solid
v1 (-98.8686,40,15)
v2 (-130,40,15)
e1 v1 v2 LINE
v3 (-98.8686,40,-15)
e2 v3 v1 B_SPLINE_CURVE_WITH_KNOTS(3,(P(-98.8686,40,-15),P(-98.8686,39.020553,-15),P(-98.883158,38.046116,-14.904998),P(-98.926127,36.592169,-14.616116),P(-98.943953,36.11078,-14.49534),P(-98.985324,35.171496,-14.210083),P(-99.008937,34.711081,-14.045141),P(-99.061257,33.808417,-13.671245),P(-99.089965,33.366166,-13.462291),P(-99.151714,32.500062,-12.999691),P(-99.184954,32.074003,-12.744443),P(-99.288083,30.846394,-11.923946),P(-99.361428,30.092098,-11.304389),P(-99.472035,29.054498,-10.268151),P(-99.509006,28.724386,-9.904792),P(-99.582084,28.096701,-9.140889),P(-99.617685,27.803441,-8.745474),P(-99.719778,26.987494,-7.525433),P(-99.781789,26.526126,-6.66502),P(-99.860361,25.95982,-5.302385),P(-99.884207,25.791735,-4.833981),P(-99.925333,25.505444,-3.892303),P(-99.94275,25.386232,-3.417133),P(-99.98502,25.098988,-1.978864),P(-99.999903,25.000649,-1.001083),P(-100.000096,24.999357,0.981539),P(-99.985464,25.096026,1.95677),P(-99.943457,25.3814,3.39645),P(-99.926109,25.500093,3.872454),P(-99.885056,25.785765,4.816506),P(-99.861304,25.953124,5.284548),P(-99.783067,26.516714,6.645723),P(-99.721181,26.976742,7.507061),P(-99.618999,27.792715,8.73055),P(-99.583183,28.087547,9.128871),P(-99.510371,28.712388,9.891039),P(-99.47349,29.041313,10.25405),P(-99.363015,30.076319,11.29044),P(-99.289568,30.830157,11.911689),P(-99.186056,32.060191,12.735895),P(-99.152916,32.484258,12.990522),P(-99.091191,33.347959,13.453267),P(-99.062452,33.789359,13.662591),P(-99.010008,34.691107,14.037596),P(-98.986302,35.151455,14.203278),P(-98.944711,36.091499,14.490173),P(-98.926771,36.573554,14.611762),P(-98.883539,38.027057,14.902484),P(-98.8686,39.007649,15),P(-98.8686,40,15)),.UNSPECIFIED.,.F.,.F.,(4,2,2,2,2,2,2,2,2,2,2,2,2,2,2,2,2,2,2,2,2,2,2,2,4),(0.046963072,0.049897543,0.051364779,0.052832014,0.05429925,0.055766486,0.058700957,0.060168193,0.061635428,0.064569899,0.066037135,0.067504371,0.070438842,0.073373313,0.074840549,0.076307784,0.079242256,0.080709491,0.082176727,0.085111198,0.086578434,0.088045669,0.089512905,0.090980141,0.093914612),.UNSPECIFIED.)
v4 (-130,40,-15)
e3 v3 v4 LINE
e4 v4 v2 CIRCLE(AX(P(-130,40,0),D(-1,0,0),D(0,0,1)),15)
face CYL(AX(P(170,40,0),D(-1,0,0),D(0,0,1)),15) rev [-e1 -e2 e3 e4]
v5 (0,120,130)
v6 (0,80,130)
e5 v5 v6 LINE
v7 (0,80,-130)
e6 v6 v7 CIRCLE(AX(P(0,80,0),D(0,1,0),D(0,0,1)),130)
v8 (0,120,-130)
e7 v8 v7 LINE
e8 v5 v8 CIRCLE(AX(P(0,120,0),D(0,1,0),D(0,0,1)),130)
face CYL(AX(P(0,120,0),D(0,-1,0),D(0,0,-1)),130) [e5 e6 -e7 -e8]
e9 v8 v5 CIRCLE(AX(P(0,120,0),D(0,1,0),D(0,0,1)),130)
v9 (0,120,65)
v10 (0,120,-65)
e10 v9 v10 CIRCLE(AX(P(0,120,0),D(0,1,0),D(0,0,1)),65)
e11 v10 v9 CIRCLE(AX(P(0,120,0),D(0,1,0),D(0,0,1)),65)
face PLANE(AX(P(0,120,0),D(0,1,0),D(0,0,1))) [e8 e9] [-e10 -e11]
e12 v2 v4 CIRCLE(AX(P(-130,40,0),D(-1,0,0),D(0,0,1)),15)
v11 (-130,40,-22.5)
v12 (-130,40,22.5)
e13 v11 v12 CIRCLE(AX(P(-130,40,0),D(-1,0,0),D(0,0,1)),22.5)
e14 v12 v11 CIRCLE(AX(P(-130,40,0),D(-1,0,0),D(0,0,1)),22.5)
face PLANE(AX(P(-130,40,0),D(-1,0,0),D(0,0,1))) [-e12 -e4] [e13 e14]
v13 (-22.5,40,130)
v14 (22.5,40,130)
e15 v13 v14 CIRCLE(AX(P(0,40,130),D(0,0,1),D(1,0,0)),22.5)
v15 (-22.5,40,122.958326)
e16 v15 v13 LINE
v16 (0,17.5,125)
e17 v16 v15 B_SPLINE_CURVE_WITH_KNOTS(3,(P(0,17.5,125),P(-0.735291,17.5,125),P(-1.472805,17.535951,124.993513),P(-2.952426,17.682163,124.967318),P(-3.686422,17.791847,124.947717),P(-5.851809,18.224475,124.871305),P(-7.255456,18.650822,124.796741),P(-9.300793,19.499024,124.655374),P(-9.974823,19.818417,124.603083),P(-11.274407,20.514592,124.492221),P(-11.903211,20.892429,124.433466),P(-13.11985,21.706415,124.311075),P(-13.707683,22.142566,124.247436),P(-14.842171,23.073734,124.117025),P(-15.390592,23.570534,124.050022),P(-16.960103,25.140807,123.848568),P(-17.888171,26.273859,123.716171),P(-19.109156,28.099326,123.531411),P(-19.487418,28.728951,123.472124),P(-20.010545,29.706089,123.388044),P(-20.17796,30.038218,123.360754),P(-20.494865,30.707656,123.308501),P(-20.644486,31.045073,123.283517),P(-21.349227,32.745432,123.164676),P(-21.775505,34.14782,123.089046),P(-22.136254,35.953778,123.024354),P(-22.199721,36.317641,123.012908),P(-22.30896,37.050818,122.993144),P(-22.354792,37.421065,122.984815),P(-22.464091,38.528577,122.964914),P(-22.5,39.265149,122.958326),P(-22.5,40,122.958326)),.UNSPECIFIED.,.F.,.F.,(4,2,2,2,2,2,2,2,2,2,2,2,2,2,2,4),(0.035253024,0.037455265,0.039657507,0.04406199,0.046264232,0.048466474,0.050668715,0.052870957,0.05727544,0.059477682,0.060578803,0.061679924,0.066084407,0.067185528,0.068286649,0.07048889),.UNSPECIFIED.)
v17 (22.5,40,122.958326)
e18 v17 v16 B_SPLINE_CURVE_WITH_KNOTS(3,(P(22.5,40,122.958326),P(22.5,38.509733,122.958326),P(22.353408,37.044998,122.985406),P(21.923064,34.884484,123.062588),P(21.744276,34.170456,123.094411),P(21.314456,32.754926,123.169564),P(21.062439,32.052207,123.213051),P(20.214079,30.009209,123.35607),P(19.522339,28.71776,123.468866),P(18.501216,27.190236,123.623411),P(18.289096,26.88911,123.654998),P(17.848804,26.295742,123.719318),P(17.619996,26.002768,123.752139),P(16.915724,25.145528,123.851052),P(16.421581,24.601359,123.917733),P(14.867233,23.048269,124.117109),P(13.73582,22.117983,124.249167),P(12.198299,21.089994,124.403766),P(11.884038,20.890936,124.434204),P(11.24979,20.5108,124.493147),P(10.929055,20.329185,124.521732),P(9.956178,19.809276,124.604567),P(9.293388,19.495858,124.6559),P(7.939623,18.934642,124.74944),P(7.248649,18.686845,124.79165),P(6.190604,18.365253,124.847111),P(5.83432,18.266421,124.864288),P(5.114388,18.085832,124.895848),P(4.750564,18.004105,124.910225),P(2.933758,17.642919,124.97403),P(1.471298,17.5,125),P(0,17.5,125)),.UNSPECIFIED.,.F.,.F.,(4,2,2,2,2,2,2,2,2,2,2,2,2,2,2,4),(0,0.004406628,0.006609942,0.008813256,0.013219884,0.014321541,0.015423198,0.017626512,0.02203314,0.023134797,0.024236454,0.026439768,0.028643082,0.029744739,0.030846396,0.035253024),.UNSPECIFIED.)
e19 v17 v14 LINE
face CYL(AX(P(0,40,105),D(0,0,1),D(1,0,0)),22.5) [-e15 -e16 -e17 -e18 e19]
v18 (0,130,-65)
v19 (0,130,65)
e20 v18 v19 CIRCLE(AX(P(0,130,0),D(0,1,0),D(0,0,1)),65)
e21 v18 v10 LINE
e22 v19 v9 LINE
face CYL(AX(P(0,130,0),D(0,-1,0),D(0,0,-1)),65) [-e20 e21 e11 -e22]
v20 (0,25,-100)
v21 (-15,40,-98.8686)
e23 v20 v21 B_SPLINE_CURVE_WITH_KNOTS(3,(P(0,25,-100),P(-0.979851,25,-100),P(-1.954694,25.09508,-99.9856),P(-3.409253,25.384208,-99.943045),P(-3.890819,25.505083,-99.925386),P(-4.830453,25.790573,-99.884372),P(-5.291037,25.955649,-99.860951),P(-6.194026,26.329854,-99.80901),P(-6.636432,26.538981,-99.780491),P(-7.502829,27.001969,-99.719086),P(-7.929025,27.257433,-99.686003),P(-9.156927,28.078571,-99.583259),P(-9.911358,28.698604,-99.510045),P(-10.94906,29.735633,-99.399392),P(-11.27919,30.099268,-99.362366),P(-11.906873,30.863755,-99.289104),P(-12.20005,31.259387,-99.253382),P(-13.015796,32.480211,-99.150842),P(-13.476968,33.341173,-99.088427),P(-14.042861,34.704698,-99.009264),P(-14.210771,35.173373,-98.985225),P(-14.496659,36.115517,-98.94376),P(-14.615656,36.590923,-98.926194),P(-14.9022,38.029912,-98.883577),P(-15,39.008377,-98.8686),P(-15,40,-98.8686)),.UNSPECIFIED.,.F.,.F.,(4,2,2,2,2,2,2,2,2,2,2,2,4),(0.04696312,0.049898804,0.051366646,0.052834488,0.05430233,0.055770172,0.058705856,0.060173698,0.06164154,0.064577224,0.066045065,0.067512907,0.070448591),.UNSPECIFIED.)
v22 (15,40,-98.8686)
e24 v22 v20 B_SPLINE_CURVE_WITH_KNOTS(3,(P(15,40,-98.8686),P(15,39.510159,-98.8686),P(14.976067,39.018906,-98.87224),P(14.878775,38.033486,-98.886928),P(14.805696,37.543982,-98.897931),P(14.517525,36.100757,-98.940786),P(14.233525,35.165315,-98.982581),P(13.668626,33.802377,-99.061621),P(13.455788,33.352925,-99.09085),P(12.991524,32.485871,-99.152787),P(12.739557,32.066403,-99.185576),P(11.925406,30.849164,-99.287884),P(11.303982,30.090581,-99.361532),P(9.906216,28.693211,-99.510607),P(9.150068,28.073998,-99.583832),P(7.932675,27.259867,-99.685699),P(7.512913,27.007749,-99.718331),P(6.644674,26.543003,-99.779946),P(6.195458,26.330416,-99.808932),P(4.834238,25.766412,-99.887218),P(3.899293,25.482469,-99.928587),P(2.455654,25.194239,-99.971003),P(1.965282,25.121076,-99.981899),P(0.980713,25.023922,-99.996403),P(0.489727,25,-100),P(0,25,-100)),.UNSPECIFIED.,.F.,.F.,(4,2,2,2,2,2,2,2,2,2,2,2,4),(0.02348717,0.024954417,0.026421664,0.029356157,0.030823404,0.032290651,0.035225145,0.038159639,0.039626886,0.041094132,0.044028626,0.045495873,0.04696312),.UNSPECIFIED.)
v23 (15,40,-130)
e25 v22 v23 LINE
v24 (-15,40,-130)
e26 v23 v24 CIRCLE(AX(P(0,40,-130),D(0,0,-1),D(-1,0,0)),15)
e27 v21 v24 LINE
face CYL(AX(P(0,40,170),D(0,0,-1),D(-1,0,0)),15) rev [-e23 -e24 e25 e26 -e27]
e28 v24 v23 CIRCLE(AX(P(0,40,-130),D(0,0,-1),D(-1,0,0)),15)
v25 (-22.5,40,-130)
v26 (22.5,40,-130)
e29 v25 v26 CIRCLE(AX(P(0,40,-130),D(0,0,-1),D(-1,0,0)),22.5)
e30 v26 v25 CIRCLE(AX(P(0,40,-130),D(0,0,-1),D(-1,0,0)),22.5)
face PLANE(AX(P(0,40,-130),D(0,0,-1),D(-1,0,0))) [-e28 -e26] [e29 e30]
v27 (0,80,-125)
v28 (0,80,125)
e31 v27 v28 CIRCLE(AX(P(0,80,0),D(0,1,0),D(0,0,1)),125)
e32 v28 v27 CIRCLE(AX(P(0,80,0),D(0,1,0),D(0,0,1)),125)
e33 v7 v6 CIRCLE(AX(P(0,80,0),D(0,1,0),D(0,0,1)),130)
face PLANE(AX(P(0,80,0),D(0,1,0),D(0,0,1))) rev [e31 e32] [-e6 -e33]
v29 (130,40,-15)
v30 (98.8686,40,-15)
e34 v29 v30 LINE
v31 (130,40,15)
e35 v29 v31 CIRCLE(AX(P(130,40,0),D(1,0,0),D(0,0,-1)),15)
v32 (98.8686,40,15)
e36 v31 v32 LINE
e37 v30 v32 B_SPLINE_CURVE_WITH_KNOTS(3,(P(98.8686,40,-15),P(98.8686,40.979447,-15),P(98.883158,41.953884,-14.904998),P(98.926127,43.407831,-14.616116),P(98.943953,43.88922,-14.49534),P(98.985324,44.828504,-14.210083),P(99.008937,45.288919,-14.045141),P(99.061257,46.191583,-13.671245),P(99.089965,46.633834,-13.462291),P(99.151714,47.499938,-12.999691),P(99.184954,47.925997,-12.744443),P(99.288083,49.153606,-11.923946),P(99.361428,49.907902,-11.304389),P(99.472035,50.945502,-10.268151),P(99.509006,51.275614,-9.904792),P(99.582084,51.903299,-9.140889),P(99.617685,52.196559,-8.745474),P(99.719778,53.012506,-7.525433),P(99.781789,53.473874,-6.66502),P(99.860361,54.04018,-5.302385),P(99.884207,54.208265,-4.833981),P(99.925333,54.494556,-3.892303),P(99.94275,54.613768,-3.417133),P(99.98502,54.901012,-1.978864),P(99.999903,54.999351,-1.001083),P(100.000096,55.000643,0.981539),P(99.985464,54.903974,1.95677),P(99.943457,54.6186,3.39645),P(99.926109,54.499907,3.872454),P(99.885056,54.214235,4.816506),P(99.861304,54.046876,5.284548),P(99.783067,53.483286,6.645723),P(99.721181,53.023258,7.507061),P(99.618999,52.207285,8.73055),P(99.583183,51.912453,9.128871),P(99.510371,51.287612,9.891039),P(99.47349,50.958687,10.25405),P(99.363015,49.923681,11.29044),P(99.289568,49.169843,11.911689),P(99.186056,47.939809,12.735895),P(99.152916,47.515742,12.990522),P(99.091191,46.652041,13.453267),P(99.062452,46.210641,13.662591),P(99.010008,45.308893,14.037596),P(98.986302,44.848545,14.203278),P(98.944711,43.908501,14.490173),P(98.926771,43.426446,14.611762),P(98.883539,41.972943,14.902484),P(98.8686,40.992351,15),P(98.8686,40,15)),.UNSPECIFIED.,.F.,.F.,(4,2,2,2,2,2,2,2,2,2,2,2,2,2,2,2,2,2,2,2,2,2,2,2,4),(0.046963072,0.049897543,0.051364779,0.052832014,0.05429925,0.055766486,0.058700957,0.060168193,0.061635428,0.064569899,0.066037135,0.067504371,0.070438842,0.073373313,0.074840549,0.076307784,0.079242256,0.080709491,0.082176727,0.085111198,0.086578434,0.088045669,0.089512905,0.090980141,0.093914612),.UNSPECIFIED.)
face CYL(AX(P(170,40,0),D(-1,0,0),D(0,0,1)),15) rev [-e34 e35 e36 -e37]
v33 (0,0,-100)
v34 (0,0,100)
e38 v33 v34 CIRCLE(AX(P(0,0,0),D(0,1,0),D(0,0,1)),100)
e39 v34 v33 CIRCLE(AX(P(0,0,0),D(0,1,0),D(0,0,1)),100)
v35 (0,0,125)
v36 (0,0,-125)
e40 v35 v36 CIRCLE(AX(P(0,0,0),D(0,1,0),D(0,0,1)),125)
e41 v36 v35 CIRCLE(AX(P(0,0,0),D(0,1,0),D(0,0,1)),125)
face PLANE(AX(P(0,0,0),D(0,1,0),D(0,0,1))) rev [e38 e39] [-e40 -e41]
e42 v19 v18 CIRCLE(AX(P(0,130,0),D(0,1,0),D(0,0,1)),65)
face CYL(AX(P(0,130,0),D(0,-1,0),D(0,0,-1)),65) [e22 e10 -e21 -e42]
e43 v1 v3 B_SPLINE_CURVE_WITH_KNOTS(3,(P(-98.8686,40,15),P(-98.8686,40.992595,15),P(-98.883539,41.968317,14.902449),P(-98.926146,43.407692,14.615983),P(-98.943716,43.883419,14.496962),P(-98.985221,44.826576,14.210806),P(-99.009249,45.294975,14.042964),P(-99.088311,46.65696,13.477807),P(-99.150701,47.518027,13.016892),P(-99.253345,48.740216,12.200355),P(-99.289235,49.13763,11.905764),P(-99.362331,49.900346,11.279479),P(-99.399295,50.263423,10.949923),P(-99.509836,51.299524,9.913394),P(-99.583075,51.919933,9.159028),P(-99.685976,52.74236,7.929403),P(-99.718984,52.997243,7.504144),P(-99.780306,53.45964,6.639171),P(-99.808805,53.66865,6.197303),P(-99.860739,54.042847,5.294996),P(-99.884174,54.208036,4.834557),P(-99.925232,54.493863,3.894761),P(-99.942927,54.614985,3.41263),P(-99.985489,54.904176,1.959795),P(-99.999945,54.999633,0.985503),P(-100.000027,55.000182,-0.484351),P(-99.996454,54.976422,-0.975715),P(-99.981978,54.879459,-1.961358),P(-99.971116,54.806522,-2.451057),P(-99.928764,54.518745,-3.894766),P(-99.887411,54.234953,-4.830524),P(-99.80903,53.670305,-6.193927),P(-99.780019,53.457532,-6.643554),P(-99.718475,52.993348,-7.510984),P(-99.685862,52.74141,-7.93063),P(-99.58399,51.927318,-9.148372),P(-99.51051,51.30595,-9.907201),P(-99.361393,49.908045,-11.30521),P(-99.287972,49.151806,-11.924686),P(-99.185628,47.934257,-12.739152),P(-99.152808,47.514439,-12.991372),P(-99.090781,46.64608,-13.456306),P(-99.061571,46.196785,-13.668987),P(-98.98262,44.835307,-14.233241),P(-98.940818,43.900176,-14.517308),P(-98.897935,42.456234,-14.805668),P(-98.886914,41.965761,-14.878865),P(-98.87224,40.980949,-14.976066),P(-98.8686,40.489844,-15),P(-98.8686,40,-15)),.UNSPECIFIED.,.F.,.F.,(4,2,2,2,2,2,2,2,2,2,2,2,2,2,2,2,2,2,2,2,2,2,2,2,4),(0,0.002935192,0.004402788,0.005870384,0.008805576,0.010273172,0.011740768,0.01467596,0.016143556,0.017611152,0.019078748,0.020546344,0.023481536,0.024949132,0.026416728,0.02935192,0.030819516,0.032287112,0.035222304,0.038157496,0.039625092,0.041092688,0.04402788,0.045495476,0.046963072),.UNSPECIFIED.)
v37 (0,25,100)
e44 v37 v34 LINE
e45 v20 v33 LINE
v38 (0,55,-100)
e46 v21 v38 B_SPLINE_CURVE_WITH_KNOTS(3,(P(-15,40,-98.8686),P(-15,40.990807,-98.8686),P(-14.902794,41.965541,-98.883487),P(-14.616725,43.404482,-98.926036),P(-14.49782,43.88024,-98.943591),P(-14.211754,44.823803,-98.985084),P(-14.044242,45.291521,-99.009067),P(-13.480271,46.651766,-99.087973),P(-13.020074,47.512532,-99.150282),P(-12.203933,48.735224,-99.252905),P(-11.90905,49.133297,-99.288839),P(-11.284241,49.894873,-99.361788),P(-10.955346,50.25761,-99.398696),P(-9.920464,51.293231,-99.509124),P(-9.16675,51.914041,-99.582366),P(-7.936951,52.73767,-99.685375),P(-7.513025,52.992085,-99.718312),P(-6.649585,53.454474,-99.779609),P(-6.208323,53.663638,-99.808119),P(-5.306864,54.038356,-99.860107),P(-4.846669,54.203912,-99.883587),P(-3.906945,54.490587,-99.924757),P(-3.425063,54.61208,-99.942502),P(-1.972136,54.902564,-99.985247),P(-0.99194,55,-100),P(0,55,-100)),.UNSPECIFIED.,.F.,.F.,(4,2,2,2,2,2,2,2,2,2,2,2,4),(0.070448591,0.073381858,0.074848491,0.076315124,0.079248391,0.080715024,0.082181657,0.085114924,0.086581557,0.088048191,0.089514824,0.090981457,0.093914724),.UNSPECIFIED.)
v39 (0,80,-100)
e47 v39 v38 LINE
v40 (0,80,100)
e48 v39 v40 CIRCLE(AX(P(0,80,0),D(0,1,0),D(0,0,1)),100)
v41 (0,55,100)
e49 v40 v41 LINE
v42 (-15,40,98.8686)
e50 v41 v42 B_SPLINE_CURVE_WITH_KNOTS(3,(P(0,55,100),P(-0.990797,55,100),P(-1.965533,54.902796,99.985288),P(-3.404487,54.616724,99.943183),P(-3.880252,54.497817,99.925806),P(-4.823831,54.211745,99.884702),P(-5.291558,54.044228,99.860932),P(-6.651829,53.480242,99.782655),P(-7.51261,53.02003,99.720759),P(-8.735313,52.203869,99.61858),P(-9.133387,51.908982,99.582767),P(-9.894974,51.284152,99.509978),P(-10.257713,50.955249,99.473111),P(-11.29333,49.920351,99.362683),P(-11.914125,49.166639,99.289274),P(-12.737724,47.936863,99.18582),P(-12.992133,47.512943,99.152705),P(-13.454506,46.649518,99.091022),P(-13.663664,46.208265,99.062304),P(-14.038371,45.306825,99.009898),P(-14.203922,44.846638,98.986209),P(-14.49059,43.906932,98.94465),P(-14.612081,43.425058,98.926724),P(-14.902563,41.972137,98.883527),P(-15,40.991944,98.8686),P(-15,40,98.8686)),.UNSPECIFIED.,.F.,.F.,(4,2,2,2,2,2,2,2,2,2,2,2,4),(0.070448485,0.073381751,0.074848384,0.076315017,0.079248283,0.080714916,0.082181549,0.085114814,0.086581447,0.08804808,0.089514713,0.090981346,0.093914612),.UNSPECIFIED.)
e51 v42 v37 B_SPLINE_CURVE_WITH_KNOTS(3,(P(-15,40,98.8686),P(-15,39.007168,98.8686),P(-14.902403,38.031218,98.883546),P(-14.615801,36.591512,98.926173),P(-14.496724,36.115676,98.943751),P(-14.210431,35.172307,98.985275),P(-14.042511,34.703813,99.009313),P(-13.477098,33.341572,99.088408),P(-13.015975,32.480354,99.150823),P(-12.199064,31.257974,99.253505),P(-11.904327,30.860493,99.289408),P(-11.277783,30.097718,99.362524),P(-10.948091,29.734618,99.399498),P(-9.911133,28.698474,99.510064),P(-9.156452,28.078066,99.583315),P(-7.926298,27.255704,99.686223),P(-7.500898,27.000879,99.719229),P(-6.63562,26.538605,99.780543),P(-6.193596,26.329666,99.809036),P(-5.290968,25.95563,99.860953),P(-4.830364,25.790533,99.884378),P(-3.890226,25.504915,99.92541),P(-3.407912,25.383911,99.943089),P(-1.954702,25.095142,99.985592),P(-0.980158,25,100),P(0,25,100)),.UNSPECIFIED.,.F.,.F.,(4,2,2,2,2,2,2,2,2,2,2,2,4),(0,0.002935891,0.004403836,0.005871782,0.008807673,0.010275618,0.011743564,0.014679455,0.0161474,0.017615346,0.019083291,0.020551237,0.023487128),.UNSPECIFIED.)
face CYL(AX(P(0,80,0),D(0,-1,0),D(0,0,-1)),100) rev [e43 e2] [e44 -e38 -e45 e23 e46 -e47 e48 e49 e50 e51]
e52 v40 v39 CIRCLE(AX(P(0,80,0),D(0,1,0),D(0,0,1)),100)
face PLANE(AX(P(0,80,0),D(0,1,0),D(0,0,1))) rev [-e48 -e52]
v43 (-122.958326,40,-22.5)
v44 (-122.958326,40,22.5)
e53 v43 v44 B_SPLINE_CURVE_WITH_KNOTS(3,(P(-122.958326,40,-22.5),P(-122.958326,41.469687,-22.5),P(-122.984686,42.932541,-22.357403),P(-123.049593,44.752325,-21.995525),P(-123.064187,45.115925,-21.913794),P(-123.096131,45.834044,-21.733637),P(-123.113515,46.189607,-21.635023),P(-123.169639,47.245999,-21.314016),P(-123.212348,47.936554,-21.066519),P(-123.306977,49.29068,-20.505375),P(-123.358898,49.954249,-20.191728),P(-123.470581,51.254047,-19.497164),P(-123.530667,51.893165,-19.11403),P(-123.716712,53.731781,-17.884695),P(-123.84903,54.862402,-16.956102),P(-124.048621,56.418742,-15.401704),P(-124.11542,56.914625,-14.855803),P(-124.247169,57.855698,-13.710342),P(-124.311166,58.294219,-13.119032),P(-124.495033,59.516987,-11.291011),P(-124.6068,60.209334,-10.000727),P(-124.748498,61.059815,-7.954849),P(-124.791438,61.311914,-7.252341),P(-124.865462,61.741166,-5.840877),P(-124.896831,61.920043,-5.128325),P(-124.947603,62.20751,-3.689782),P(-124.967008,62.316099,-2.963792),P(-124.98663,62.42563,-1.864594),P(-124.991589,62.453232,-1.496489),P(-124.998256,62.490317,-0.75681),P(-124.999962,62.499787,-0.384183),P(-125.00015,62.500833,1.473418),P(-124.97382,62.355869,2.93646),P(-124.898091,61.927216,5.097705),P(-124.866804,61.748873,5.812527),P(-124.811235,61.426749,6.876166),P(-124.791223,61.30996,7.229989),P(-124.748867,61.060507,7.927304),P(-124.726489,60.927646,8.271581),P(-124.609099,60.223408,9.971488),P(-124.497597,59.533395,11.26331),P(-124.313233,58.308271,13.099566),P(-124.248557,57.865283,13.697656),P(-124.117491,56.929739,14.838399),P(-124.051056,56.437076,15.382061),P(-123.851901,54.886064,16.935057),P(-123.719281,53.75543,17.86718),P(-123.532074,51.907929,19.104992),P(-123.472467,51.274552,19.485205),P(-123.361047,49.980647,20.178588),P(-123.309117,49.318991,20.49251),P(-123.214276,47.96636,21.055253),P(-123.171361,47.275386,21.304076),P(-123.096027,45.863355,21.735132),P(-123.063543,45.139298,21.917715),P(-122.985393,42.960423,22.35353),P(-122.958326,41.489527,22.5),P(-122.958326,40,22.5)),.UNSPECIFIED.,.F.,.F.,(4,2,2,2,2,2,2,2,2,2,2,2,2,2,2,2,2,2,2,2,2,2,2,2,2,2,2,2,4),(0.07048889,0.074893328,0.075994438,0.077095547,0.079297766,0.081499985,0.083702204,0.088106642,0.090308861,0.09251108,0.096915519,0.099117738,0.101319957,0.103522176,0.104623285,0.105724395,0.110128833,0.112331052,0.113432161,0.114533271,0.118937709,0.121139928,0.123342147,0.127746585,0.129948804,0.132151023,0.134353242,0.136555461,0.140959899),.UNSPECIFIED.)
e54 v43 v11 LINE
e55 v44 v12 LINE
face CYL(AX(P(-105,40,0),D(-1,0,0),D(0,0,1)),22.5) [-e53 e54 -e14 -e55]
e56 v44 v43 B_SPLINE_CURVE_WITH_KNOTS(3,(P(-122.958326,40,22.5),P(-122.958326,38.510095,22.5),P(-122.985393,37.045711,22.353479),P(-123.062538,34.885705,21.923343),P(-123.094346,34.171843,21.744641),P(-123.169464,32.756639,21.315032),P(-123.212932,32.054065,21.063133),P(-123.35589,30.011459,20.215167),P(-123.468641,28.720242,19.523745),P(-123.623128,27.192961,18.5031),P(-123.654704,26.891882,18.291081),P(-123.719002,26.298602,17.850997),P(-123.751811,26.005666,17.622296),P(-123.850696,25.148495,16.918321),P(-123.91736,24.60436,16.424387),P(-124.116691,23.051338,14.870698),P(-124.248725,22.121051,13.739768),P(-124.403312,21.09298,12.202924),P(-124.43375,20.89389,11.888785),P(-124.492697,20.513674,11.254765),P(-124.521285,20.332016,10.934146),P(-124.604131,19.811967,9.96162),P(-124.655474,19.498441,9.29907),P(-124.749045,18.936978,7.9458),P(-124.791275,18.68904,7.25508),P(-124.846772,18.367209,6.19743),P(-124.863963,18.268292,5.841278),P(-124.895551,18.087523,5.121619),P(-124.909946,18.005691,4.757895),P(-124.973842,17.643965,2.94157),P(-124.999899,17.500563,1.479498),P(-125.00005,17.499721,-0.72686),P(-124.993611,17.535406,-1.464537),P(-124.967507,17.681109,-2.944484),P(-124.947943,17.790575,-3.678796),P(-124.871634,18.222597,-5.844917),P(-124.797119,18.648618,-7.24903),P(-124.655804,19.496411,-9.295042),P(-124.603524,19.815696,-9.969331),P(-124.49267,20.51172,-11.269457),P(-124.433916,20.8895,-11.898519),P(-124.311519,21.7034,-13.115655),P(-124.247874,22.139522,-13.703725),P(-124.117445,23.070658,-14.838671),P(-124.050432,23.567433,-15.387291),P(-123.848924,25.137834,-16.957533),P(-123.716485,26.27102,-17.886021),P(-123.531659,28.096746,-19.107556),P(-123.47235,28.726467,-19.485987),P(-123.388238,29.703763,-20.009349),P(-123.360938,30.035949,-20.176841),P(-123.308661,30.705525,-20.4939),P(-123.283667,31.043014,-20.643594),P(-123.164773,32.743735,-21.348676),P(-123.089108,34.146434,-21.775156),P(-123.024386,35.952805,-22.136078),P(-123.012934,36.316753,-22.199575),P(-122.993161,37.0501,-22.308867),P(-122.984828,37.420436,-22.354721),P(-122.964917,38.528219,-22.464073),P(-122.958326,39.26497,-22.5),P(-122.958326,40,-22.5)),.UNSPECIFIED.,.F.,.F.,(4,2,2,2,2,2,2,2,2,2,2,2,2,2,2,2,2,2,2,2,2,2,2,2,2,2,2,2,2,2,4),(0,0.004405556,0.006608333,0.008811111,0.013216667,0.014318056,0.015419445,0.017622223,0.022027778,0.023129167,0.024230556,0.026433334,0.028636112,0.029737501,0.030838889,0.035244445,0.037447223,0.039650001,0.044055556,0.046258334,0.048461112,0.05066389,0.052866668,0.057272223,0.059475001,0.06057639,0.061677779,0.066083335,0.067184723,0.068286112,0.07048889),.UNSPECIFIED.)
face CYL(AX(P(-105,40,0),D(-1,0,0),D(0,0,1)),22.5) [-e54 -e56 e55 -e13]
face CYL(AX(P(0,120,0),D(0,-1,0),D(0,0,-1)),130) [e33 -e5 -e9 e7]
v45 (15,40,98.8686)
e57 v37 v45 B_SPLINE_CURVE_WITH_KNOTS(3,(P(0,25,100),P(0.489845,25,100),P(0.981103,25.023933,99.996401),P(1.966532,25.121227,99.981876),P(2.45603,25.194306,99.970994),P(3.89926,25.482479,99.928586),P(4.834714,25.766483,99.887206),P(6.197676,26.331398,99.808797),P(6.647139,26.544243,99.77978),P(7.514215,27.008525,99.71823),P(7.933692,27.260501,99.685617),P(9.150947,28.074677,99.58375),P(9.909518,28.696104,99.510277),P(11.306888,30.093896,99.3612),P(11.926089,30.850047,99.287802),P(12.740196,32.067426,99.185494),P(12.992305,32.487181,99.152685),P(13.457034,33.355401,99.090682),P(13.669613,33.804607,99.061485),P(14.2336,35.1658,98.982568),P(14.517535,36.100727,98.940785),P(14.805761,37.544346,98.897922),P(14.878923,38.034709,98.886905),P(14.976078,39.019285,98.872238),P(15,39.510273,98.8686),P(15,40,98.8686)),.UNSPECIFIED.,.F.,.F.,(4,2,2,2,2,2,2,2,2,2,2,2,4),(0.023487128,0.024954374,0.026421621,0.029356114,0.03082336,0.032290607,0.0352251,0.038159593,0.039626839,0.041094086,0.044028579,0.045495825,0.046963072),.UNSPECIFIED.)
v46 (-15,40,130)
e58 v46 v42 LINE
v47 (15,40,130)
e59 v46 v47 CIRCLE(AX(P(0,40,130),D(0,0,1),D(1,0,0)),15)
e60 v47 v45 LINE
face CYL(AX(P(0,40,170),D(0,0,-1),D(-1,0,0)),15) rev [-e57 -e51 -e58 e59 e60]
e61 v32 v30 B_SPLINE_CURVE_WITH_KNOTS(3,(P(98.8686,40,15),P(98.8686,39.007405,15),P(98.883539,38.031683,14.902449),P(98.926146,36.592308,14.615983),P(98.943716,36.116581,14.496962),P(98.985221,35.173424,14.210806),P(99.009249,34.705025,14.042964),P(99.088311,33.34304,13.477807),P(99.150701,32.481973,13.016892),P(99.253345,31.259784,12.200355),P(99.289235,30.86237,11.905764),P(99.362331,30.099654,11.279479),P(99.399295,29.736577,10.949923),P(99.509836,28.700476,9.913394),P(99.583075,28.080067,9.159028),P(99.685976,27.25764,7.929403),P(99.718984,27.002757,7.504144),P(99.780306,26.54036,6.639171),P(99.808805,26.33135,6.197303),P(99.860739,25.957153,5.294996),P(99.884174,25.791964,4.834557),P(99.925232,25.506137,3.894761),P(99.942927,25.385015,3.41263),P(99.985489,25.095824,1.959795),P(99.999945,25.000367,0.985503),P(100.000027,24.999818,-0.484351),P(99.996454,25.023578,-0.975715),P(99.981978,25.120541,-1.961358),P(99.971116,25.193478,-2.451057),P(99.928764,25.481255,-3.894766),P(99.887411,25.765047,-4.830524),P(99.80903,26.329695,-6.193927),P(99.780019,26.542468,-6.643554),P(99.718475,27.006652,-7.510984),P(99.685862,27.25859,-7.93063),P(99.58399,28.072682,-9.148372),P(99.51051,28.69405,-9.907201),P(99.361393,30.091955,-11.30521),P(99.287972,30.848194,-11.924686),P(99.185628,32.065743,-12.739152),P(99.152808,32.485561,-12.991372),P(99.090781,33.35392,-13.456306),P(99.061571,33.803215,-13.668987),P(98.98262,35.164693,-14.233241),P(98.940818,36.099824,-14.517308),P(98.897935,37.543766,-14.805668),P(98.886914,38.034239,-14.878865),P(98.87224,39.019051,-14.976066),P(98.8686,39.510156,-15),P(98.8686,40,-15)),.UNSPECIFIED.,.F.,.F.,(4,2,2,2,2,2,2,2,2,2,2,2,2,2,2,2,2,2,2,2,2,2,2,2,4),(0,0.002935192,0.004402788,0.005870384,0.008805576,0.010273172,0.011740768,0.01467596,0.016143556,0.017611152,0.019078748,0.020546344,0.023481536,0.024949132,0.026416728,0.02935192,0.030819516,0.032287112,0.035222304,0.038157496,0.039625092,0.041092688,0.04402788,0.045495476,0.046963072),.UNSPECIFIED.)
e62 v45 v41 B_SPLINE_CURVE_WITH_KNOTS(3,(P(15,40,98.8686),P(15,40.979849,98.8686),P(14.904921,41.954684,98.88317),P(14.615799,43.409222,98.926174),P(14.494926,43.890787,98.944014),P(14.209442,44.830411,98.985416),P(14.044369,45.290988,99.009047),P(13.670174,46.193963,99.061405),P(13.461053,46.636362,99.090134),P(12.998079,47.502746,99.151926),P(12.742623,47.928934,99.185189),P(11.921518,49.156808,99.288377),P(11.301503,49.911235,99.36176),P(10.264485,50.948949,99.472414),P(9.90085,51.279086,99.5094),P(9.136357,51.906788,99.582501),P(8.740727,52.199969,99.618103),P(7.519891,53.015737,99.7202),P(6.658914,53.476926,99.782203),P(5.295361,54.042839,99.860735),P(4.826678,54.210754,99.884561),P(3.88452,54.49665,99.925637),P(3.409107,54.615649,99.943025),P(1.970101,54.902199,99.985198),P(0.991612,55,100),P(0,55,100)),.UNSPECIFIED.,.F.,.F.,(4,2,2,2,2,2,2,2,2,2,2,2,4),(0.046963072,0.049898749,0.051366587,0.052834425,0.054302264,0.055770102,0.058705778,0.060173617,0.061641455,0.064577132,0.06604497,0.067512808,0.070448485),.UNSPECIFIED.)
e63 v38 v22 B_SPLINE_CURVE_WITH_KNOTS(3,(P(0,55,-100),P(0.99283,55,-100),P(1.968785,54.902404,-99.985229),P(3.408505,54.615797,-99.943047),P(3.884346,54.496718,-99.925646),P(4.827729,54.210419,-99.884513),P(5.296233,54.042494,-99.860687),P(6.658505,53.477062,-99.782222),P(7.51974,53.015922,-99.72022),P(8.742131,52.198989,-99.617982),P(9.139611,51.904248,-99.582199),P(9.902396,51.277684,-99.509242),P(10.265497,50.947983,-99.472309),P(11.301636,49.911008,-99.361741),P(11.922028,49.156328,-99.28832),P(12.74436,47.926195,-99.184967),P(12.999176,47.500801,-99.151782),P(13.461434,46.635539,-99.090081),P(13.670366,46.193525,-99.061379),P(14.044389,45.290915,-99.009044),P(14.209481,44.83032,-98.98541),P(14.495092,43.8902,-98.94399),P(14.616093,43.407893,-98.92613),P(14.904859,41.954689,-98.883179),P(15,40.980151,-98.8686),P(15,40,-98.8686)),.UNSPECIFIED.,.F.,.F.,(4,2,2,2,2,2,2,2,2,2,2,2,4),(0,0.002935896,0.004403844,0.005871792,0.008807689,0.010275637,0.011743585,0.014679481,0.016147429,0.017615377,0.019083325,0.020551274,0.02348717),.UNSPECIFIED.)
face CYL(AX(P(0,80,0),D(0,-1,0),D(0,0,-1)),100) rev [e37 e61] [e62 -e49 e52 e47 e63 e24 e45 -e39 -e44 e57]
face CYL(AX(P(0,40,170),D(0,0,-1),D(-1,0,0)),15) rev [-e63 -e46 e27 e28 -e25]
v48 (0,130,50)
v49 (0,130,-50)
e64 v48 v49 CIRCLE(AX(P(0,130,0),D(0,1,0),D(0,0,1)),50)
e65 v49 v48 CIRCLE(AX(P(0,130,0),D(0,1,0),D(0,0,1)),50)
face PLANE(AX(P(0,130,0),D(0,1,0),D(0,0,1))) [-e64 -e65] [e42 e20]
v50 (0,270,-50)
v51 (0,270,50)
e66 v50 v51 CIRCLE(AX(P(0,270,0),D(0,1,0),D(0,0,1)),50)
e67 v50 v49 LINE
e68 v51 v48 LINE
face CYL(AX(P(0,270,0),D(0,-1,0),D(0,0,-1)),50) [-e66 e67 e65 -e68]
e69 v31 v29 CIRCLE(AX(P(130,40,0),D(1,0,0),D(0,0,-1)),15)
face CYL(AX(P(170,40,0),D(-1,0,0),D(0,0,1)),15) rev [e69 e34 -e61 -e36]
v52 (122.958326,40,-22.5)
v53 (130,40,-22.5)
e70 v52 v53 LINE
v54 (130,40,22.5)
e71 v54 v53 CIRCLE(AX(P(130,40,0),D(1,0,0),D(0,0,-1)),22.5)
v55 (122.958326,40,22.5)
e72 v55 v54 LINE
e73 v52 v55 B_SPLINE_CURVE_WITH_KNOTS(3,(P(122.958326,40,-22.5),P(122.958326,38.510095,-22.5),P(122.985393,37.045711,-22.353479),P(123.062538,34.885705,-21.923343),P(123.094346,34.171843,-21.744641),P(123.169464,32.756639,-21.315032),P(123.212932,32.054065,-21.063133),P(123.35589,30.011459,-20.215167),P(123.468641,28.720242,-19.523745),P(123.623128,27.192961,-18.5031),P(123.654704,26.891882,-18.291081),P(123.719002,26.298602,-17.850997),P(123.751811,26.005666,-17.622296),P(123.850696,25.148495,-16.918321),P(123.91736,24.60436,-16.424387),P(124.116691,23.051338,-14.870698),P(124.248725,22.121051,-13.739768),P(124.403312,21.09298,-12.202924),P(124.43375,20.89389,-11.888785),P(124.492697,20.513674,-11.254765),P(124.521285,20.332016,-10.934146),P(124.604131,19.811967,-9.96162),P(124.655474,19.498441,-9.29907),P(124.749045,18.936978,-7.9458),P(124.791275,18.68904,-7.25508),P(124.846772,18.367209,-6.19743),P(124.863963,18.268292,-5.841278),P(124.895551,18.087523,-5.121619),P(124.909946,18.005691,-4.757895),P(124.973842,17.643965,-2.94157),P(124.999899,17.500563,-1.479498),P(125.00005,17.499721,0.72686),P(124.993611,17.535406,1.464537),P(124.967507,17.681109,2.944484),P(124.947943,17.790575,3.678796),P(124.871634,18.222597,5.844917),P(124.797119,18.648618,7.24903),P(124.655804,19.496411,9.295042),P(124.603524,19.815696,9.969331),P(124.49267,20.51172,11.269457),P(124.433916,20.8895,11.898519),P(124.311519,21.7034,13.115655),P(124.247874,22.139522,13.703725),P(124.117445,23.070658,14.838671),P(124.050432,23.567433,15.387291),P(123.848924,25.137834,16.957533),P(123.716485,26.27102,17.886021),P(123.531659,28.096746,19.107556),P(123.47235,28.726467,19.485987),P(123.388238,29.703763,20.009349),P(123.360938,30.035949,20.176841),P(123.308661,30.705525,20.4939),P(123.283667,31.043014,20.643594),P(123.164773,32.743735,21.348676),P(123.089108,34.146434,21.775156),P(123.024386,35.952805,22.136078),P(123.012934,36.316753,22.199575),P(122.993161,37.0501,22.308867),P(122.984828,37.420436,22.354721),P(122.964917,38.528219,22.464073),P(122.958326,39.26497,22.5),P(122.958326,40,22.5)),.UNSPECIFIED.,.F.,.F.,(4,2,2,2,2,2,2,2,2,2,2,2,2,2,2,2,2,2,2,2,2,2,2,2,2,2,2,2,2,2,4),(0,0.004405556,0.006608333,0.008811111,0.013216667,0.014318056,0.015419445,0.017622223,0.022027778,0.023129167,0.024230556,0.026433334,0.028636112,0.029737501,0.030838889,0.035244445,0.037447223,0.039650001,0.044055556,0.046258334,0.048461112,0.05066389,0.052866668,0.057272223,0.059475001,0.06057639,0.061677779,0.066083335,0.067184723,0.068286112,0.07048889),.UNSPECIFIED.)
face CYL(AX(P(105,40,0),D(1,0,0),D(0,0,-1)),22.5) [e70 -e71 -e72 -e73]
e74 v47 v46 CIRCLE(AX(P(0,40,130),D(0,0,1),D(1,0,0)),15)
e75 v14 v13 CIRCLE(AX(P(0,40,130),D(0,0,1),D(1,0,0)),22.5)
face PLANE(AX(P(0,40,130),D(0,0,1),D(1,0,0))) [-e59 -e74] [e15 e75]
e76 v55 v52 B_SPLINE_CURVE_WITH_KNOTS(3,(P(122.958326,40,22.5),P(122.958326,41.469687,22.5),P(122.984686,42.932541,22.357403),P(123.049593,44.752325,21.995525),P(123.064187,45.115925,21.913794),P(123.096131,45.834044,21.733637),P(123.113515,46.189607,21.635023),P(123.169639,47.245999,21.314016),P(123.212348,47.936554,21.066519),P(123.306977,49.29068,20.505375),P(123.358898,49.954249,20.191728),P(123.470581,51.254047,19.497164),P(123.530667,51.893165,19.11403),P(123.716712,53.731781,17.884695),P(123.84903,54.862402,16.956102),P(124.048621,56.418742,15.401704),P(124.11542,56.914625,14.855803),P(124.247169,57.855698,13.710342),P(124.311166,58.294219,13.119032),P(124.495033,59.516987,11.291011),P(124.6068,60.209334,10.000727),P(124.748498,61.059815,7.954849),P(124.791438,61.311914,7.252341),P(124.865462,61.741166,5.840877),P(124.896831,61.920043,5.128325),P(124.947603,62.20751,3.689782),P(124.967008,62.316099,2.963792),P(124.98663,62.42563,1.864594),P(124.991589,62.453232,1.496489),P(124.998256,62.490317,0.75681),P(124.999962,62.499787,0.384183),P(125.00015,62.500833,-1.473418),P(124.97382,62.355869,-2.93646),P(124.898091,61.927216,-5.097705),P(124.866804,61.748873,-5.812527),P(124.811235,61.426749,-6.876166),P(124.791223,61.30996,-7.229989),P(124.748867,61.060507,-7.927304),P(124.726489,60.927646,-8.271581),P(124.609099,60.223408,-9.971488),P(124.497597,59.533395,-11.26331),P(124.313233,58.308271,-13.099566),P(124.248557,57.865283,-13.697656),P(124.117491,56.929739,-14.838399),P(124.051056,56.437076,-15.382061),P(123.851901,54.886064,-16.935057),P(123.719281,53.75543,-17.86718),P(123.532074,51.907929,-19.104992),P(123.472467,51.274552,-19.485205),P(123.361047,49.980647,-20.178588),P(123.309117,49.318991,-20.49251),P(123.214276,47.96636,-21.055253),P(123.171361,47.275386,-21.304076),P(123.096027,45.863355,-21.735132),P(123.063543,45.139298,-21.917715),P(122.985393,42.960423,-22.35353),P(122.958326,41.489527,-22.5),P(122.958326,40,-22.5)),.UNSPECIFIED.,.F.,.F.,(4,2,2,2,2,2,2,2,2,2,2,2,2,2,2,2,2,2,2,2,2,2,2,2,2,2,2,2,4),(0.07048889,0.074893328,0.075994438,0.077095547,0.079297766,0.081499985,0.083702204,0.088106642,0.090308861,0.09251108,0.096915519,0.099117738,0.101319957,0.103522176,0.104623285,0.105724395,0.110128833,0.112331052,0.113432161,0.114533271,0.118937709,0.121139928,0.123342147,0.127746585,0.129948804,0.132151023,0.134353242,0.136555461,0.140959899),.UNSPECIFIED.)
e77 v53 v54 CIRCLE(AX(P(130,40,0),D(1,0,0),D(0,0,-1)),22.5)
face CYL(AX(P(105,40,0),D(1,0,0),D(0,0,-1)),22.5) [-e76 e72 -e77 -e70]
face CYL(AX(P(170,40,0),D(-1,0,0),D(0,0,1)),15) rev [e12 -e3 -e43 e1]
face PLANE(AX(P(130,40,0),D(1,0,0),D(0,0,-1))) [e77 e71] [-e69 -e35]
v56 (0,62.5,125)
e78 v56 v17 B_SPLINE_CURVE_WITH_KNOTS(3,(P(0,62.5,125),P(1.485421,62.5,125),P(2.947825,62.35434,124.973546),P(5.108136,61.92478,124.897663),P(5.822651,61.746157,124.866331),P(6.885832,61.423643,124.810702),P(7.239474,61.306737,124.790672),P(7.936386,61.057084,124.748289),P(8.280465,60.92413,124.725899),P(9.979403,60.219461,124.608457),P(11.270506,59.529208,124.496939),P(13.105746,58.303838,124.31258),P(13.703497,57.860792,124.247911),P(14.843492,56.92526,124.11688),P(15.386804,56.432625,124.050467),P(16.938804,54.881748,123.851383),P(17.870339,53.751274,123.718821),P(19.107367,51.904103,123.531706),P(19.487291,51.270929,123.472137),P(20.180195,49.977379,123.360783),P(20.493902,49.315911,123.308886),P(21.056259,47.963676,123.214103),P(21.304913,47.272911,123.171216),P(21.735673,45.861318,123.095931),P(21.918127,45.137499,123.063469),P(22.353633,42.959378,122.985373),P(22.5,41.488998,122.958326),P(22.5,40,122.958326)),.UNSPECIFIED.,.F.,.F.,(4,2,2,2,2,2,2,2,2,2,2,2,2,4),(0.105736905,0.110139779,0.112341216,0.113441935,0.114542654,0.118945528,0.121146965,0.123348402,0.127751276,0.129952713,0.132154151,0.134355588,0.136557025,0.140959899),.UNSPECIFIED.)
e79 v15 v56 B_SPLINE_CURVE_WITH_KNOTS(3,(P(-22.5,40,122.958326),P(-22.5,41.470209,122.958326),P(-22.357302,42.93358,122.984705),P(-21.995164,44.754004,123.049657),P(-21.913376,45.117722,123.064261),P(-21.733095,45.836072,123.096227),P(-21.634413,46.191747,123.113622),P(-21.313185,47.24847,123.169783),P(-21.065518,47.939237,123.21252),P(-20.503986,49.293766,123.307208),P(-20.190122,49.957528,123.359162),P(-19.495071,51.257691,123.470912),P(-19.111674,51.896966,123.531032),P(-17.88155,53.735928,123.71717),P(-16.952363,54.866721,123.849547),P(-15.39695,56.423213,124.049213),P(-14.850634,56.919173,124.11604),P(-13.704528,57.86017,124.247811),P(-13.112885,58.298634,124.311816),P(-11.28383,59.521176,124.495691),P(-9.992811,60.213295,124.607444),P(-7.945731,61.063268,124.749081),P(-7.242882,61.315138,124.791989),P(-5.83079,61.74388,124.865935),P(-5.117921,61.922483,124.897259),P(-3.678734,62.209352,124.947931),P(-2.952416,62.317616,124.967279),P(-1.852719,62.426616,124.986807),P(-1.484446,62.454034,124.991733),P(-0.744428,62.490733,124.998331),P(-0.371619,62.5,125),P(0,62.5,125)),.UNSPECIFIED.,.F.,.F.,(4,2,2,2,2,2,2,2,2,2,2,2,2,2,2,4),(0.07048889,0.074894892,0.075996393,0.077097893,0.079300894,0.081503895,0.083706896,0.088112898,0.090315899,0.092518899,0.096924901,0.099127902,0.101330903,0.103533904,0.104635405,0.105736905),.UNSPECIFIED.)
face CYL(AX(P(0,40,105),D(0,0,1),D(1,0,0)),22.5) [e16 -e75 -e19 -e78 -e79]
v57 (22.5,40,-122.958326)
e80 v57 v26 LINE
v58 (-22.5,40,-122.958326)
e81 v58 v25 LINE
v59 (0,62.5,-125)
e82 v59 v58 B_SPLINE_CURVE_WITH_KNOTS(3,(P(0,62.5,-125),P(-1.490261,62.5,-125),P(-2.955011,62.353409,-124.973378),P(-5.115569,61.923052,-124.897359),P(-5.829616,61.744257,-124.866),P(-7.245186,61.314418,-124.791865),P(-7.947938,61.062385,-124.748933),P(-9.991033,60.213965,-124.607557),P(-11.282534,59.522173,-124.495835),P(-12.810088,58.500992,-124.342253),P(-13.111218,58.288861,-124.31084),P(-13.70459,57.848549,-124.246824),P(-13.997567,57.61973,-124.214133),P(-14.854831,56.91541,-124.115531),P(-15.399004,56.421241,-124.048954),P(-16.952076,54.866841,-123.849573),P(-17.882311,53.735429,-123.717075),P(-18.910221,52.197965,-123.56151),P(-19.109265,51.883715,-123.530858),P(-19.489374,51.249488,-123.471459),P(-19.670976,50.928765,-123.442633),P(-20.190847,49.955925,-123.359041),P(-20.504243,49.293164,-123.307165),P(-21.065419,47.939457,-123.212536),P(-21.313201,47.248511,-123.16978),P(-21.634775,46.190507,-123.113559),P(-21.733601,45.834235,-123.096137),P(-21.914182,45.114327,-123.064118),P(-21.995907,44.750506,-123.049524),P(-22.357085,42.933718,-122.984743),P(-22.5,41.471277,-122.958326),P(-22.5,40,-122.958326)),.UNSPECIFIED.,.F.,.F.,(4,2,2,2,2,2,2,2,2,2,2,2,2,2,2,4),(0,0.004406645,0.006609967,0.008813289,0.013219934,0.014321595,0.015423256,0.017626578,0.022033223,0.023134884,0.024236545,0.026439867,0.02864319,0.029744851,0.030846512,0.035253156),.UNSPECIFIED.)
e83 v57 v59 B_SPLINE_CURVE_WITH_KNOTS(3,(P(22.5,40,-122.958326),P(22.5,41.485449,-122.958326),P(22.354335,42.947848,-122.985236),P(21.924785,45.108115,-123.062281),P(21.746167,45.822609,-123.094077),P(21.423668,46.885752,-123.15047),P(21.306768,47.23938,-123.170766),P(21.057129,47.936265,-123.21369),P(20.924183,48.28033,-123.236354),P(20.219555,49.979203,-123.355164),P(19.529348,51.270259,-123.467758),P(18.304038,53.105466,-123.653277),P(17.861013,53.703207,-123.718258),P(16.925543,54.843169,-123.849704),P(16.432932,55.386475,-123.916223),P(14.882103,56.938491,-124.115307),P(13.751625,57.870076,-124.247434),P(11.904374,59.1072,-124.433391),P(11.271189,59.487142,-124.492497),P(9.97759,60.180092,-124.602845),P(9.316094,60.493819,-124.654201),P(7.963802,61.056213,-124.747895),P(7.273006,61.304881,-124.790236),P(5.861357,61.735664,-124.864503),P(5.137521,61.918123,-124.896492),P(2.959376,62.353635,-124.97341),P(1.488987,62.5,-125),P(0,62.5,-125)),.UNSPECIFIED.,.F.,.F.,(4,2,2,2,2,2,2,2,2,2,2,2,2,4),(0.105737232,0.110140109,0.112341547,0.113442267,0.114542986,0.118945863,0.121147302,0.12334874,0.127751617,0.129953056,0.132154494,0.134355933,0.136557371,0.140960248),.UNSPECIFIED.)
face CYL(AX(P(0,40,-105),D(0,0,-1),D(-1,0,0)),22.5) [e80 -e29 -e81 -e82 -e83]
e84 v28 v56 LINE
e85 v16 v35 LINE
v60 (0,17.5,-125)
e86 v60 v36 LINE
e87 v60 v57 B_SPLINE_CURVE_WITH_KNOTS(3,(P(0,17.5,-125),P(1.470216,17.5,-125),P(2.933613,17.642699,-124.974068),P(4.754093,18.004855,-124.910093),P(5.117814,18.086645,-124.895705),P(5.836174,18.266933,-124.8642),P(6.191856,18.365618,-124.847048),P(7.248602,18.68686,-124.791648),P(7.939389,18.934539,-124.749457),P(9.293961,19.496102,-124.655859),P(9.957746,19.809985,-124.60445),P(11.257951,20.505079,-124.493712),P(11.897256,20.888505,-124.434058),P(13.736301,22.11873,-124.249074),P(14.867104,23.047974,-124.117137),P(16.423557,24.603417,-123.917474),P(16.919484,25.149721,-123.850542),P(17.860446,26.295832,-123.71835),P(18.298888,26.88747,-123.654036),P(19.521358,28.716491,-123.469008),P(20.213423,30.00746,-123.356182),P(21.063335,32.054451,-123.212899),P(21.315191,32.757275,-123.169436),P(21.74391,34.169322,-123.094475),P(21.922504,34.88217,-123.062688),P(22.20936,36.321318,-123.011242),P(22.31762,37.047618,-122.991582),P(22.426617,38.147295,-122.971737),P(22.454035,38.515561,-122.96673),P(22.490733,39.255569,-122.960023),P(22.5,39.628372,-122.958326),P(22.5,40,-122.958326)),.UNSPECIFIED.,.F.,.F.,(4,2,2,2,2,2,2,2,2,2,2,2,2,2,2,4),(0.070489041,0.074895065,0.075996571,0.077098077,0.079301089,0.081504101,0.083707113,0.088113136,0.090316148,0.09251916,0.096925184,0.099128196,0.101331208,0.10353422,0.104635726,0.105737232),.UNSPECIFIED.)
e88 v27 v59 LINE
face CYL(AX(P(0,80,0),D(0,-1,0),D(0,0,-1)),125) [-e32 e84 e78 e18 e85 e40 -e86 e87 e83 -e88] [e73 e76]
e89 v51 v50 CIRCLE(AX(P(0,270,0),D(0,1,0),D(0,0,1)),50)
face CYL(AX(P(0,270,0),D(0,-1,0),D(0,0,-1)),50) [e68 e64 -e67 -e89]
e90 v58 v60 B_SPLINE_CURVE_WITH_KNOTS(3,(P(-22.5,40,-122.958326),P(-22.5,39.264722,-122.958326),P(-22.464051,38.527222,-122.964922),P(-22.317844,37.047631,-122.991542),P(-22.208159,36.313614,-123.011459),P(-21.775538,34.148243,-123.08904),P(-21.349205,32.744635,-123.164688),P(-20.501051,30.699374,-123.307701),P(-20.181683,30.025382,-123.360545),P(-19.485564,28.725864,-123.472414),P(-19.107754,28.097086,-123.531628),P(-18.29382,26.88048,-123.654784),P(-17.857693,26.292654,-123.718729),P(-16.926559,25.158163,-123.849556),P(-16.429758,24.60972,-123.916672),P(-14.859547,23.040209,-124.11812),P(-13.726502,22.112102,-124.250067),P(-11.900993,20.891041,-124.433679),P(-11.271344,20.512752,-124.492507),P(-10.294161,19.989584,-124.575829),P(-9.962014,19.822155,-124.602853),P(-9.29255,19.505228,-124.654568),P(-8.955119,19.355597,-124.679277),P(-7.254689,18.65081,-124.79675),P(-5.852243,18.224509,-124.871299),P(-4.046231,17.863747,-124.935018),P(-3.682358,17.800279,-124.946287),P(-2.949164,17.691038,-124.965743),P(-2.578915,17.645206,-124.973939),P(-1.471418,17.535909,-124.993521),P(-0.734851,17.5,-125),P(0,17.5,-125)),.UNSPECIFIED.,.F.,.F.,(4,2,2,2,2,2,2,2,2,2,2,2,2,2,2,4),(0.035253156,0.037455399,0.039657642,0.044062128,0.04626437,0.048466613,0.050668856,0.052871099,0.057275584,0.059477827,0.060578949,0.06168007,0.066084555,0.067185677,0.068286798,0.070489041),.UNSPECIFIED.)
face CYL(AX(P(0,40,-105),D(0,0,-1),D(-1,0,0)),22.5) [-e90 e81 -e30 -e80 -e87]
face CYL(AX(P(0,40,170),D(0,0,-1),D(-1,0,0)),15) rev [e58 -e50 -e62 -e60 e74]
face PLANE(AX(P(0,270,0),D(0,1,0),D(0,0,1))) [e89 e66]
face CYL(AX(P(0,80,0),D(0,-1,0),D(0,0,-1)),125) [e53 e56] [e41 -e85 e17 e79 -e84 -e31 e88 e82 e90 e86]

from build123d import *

# Parameters (mm, degrees)
SKETCH1_R           = 125
SKETCH1_R_2         = 100
BOSS_EXTRUDE1_DEPTH = 80
SKETCH2_R           = 130
BOSS_EXTRUDE2_DEPTH = 40
SKETCH3_R           = 50
BOSS_EXTRUDE3_DEPTH = 150
SKETCH4_R           = 65
BOSS_EXTRUDE4_DEPTH = 10
SKETCH5_R           = 15
CUT_EXTRUDE1_DEPTH  = 170
CIRPATTERN1_COUNT   = 4
BOSS_EXTRUDE5_START = -20
SKETCH6_R           = 22.5
SKETCH6_R_2         = 15
BOSS_EXTRUDE5_DEPTH = 25
CIRPATTERN2_COUNT   = 4


with BuildPart() as part:
    # Sketch1 → Boss-Extrude1 (new body)
    with BuildSketch(Plane(origin=(0, 0, 0), x_dir=(1, 0, 0), z_dir=(0, 1, 0))):
        with Locations(Location((0, 0, 0), (0, 0, 270))):
            Circle(SKETCH1_R)
        with Locations(Location((0, 0, 0), (0, 0, 270))):
            Circle(SKETCH1_R_2, mode=Mode.SUBTRACT)
    extrude(amount=BOSS_EXTRUDE1_DEPTH)

    # Sketch2 → Boss-Extrude2 (add)
    with BuildSketch(Plane(origin=(0, 80, 0), x_dir=(1, 0, 0), z_dir=(0, 1, 0))):
        with Locations(Location((0, 0, 0), (0, 0, 270))):
            Circle(SKETCH2_R)
    extrude(amount=BOSS_EXTRUDE2_DEPTH)

    # Sketch3 → Boss-Extrude3 (add)
    with BuildSketch(Plane(origin=(0, 120, 0), x_dir=(1, 0, 0), z_dir=(0, 1, 0))):
        with Locations(Location((0, 0, 0), (0, 0, 270))):
            Circle(SKETCH3_R)
    extrude(amount=BOSS_EXTRUDE3_DEPTH)

    # Sketch4 → Boss-Extrude4 (add)
    with BuildSketch(Plane(origin=(0, 120, 0), x_dir=(1, 0, 0), z_dir=(0, 1, 0))):
        with Locations(Location((0, 0, 0), (0, 0, 270))):
            Circle(SKETCH4_R)
    extrude(amount=BOSS_EXTRUDE4_DEPTH)

    # Sketch5 → Cut-Extrude1 (cut, symmetric)
    with BuildSketch(Plane(origin=(0, 0, 0), x_dir=(0, 0, -1), z_dir=(1, 0, 0))):
        with Locations(Location((0, 40, 0), (0, 0, 180))):
            Circle(SKETCH5_R)
    cut_extrude1 = extrude(amount=CUT_EXTRUDE1_DEPTH, both=True, mode=Mode.SUBTRACT)

    # CirPattern1: Cut-Extrude1 ×4 about axis
    cirpattern1_axis = Axis((0, 80, 0), (0, -1, 0))
    for i in range(1, CIRPATTERN1_COUNT):
        add(cut_extrude1.rotate(cirpattern1_axis, i * 360 / CIRPATTERN1_COUNT), mode=Mode.SUBTRACT)

    # Sketch6 → Boss-Extrude5 (add)
    with BuildSketch(Plane.ZY.offset(125).offset(BOSS_EXTRUDE5_START)):
        with Locations((0, 40)):
            Circle(SKETCH6_R)
        with Locations((0, 40)):
            Circle(SKETCH6_R_2, mode=Mode.SUBTRACT)
    boss_extrude5 = extrude(amount=BOSS_EXTRUDE5_DEPTH)

    # CirPattern2: Boss-Extrude5 ×4 about axis
    cirpattern2_axis = Axis((0, 0, 0), (0, 1, 0))
    for i in range(1, CIRPATTERN2_COUNT):
        add(boss_extrude5.rotate(cirpattern2_axis, i * 360 / CIRPATTERN2_COUNT))


solid = part.part
